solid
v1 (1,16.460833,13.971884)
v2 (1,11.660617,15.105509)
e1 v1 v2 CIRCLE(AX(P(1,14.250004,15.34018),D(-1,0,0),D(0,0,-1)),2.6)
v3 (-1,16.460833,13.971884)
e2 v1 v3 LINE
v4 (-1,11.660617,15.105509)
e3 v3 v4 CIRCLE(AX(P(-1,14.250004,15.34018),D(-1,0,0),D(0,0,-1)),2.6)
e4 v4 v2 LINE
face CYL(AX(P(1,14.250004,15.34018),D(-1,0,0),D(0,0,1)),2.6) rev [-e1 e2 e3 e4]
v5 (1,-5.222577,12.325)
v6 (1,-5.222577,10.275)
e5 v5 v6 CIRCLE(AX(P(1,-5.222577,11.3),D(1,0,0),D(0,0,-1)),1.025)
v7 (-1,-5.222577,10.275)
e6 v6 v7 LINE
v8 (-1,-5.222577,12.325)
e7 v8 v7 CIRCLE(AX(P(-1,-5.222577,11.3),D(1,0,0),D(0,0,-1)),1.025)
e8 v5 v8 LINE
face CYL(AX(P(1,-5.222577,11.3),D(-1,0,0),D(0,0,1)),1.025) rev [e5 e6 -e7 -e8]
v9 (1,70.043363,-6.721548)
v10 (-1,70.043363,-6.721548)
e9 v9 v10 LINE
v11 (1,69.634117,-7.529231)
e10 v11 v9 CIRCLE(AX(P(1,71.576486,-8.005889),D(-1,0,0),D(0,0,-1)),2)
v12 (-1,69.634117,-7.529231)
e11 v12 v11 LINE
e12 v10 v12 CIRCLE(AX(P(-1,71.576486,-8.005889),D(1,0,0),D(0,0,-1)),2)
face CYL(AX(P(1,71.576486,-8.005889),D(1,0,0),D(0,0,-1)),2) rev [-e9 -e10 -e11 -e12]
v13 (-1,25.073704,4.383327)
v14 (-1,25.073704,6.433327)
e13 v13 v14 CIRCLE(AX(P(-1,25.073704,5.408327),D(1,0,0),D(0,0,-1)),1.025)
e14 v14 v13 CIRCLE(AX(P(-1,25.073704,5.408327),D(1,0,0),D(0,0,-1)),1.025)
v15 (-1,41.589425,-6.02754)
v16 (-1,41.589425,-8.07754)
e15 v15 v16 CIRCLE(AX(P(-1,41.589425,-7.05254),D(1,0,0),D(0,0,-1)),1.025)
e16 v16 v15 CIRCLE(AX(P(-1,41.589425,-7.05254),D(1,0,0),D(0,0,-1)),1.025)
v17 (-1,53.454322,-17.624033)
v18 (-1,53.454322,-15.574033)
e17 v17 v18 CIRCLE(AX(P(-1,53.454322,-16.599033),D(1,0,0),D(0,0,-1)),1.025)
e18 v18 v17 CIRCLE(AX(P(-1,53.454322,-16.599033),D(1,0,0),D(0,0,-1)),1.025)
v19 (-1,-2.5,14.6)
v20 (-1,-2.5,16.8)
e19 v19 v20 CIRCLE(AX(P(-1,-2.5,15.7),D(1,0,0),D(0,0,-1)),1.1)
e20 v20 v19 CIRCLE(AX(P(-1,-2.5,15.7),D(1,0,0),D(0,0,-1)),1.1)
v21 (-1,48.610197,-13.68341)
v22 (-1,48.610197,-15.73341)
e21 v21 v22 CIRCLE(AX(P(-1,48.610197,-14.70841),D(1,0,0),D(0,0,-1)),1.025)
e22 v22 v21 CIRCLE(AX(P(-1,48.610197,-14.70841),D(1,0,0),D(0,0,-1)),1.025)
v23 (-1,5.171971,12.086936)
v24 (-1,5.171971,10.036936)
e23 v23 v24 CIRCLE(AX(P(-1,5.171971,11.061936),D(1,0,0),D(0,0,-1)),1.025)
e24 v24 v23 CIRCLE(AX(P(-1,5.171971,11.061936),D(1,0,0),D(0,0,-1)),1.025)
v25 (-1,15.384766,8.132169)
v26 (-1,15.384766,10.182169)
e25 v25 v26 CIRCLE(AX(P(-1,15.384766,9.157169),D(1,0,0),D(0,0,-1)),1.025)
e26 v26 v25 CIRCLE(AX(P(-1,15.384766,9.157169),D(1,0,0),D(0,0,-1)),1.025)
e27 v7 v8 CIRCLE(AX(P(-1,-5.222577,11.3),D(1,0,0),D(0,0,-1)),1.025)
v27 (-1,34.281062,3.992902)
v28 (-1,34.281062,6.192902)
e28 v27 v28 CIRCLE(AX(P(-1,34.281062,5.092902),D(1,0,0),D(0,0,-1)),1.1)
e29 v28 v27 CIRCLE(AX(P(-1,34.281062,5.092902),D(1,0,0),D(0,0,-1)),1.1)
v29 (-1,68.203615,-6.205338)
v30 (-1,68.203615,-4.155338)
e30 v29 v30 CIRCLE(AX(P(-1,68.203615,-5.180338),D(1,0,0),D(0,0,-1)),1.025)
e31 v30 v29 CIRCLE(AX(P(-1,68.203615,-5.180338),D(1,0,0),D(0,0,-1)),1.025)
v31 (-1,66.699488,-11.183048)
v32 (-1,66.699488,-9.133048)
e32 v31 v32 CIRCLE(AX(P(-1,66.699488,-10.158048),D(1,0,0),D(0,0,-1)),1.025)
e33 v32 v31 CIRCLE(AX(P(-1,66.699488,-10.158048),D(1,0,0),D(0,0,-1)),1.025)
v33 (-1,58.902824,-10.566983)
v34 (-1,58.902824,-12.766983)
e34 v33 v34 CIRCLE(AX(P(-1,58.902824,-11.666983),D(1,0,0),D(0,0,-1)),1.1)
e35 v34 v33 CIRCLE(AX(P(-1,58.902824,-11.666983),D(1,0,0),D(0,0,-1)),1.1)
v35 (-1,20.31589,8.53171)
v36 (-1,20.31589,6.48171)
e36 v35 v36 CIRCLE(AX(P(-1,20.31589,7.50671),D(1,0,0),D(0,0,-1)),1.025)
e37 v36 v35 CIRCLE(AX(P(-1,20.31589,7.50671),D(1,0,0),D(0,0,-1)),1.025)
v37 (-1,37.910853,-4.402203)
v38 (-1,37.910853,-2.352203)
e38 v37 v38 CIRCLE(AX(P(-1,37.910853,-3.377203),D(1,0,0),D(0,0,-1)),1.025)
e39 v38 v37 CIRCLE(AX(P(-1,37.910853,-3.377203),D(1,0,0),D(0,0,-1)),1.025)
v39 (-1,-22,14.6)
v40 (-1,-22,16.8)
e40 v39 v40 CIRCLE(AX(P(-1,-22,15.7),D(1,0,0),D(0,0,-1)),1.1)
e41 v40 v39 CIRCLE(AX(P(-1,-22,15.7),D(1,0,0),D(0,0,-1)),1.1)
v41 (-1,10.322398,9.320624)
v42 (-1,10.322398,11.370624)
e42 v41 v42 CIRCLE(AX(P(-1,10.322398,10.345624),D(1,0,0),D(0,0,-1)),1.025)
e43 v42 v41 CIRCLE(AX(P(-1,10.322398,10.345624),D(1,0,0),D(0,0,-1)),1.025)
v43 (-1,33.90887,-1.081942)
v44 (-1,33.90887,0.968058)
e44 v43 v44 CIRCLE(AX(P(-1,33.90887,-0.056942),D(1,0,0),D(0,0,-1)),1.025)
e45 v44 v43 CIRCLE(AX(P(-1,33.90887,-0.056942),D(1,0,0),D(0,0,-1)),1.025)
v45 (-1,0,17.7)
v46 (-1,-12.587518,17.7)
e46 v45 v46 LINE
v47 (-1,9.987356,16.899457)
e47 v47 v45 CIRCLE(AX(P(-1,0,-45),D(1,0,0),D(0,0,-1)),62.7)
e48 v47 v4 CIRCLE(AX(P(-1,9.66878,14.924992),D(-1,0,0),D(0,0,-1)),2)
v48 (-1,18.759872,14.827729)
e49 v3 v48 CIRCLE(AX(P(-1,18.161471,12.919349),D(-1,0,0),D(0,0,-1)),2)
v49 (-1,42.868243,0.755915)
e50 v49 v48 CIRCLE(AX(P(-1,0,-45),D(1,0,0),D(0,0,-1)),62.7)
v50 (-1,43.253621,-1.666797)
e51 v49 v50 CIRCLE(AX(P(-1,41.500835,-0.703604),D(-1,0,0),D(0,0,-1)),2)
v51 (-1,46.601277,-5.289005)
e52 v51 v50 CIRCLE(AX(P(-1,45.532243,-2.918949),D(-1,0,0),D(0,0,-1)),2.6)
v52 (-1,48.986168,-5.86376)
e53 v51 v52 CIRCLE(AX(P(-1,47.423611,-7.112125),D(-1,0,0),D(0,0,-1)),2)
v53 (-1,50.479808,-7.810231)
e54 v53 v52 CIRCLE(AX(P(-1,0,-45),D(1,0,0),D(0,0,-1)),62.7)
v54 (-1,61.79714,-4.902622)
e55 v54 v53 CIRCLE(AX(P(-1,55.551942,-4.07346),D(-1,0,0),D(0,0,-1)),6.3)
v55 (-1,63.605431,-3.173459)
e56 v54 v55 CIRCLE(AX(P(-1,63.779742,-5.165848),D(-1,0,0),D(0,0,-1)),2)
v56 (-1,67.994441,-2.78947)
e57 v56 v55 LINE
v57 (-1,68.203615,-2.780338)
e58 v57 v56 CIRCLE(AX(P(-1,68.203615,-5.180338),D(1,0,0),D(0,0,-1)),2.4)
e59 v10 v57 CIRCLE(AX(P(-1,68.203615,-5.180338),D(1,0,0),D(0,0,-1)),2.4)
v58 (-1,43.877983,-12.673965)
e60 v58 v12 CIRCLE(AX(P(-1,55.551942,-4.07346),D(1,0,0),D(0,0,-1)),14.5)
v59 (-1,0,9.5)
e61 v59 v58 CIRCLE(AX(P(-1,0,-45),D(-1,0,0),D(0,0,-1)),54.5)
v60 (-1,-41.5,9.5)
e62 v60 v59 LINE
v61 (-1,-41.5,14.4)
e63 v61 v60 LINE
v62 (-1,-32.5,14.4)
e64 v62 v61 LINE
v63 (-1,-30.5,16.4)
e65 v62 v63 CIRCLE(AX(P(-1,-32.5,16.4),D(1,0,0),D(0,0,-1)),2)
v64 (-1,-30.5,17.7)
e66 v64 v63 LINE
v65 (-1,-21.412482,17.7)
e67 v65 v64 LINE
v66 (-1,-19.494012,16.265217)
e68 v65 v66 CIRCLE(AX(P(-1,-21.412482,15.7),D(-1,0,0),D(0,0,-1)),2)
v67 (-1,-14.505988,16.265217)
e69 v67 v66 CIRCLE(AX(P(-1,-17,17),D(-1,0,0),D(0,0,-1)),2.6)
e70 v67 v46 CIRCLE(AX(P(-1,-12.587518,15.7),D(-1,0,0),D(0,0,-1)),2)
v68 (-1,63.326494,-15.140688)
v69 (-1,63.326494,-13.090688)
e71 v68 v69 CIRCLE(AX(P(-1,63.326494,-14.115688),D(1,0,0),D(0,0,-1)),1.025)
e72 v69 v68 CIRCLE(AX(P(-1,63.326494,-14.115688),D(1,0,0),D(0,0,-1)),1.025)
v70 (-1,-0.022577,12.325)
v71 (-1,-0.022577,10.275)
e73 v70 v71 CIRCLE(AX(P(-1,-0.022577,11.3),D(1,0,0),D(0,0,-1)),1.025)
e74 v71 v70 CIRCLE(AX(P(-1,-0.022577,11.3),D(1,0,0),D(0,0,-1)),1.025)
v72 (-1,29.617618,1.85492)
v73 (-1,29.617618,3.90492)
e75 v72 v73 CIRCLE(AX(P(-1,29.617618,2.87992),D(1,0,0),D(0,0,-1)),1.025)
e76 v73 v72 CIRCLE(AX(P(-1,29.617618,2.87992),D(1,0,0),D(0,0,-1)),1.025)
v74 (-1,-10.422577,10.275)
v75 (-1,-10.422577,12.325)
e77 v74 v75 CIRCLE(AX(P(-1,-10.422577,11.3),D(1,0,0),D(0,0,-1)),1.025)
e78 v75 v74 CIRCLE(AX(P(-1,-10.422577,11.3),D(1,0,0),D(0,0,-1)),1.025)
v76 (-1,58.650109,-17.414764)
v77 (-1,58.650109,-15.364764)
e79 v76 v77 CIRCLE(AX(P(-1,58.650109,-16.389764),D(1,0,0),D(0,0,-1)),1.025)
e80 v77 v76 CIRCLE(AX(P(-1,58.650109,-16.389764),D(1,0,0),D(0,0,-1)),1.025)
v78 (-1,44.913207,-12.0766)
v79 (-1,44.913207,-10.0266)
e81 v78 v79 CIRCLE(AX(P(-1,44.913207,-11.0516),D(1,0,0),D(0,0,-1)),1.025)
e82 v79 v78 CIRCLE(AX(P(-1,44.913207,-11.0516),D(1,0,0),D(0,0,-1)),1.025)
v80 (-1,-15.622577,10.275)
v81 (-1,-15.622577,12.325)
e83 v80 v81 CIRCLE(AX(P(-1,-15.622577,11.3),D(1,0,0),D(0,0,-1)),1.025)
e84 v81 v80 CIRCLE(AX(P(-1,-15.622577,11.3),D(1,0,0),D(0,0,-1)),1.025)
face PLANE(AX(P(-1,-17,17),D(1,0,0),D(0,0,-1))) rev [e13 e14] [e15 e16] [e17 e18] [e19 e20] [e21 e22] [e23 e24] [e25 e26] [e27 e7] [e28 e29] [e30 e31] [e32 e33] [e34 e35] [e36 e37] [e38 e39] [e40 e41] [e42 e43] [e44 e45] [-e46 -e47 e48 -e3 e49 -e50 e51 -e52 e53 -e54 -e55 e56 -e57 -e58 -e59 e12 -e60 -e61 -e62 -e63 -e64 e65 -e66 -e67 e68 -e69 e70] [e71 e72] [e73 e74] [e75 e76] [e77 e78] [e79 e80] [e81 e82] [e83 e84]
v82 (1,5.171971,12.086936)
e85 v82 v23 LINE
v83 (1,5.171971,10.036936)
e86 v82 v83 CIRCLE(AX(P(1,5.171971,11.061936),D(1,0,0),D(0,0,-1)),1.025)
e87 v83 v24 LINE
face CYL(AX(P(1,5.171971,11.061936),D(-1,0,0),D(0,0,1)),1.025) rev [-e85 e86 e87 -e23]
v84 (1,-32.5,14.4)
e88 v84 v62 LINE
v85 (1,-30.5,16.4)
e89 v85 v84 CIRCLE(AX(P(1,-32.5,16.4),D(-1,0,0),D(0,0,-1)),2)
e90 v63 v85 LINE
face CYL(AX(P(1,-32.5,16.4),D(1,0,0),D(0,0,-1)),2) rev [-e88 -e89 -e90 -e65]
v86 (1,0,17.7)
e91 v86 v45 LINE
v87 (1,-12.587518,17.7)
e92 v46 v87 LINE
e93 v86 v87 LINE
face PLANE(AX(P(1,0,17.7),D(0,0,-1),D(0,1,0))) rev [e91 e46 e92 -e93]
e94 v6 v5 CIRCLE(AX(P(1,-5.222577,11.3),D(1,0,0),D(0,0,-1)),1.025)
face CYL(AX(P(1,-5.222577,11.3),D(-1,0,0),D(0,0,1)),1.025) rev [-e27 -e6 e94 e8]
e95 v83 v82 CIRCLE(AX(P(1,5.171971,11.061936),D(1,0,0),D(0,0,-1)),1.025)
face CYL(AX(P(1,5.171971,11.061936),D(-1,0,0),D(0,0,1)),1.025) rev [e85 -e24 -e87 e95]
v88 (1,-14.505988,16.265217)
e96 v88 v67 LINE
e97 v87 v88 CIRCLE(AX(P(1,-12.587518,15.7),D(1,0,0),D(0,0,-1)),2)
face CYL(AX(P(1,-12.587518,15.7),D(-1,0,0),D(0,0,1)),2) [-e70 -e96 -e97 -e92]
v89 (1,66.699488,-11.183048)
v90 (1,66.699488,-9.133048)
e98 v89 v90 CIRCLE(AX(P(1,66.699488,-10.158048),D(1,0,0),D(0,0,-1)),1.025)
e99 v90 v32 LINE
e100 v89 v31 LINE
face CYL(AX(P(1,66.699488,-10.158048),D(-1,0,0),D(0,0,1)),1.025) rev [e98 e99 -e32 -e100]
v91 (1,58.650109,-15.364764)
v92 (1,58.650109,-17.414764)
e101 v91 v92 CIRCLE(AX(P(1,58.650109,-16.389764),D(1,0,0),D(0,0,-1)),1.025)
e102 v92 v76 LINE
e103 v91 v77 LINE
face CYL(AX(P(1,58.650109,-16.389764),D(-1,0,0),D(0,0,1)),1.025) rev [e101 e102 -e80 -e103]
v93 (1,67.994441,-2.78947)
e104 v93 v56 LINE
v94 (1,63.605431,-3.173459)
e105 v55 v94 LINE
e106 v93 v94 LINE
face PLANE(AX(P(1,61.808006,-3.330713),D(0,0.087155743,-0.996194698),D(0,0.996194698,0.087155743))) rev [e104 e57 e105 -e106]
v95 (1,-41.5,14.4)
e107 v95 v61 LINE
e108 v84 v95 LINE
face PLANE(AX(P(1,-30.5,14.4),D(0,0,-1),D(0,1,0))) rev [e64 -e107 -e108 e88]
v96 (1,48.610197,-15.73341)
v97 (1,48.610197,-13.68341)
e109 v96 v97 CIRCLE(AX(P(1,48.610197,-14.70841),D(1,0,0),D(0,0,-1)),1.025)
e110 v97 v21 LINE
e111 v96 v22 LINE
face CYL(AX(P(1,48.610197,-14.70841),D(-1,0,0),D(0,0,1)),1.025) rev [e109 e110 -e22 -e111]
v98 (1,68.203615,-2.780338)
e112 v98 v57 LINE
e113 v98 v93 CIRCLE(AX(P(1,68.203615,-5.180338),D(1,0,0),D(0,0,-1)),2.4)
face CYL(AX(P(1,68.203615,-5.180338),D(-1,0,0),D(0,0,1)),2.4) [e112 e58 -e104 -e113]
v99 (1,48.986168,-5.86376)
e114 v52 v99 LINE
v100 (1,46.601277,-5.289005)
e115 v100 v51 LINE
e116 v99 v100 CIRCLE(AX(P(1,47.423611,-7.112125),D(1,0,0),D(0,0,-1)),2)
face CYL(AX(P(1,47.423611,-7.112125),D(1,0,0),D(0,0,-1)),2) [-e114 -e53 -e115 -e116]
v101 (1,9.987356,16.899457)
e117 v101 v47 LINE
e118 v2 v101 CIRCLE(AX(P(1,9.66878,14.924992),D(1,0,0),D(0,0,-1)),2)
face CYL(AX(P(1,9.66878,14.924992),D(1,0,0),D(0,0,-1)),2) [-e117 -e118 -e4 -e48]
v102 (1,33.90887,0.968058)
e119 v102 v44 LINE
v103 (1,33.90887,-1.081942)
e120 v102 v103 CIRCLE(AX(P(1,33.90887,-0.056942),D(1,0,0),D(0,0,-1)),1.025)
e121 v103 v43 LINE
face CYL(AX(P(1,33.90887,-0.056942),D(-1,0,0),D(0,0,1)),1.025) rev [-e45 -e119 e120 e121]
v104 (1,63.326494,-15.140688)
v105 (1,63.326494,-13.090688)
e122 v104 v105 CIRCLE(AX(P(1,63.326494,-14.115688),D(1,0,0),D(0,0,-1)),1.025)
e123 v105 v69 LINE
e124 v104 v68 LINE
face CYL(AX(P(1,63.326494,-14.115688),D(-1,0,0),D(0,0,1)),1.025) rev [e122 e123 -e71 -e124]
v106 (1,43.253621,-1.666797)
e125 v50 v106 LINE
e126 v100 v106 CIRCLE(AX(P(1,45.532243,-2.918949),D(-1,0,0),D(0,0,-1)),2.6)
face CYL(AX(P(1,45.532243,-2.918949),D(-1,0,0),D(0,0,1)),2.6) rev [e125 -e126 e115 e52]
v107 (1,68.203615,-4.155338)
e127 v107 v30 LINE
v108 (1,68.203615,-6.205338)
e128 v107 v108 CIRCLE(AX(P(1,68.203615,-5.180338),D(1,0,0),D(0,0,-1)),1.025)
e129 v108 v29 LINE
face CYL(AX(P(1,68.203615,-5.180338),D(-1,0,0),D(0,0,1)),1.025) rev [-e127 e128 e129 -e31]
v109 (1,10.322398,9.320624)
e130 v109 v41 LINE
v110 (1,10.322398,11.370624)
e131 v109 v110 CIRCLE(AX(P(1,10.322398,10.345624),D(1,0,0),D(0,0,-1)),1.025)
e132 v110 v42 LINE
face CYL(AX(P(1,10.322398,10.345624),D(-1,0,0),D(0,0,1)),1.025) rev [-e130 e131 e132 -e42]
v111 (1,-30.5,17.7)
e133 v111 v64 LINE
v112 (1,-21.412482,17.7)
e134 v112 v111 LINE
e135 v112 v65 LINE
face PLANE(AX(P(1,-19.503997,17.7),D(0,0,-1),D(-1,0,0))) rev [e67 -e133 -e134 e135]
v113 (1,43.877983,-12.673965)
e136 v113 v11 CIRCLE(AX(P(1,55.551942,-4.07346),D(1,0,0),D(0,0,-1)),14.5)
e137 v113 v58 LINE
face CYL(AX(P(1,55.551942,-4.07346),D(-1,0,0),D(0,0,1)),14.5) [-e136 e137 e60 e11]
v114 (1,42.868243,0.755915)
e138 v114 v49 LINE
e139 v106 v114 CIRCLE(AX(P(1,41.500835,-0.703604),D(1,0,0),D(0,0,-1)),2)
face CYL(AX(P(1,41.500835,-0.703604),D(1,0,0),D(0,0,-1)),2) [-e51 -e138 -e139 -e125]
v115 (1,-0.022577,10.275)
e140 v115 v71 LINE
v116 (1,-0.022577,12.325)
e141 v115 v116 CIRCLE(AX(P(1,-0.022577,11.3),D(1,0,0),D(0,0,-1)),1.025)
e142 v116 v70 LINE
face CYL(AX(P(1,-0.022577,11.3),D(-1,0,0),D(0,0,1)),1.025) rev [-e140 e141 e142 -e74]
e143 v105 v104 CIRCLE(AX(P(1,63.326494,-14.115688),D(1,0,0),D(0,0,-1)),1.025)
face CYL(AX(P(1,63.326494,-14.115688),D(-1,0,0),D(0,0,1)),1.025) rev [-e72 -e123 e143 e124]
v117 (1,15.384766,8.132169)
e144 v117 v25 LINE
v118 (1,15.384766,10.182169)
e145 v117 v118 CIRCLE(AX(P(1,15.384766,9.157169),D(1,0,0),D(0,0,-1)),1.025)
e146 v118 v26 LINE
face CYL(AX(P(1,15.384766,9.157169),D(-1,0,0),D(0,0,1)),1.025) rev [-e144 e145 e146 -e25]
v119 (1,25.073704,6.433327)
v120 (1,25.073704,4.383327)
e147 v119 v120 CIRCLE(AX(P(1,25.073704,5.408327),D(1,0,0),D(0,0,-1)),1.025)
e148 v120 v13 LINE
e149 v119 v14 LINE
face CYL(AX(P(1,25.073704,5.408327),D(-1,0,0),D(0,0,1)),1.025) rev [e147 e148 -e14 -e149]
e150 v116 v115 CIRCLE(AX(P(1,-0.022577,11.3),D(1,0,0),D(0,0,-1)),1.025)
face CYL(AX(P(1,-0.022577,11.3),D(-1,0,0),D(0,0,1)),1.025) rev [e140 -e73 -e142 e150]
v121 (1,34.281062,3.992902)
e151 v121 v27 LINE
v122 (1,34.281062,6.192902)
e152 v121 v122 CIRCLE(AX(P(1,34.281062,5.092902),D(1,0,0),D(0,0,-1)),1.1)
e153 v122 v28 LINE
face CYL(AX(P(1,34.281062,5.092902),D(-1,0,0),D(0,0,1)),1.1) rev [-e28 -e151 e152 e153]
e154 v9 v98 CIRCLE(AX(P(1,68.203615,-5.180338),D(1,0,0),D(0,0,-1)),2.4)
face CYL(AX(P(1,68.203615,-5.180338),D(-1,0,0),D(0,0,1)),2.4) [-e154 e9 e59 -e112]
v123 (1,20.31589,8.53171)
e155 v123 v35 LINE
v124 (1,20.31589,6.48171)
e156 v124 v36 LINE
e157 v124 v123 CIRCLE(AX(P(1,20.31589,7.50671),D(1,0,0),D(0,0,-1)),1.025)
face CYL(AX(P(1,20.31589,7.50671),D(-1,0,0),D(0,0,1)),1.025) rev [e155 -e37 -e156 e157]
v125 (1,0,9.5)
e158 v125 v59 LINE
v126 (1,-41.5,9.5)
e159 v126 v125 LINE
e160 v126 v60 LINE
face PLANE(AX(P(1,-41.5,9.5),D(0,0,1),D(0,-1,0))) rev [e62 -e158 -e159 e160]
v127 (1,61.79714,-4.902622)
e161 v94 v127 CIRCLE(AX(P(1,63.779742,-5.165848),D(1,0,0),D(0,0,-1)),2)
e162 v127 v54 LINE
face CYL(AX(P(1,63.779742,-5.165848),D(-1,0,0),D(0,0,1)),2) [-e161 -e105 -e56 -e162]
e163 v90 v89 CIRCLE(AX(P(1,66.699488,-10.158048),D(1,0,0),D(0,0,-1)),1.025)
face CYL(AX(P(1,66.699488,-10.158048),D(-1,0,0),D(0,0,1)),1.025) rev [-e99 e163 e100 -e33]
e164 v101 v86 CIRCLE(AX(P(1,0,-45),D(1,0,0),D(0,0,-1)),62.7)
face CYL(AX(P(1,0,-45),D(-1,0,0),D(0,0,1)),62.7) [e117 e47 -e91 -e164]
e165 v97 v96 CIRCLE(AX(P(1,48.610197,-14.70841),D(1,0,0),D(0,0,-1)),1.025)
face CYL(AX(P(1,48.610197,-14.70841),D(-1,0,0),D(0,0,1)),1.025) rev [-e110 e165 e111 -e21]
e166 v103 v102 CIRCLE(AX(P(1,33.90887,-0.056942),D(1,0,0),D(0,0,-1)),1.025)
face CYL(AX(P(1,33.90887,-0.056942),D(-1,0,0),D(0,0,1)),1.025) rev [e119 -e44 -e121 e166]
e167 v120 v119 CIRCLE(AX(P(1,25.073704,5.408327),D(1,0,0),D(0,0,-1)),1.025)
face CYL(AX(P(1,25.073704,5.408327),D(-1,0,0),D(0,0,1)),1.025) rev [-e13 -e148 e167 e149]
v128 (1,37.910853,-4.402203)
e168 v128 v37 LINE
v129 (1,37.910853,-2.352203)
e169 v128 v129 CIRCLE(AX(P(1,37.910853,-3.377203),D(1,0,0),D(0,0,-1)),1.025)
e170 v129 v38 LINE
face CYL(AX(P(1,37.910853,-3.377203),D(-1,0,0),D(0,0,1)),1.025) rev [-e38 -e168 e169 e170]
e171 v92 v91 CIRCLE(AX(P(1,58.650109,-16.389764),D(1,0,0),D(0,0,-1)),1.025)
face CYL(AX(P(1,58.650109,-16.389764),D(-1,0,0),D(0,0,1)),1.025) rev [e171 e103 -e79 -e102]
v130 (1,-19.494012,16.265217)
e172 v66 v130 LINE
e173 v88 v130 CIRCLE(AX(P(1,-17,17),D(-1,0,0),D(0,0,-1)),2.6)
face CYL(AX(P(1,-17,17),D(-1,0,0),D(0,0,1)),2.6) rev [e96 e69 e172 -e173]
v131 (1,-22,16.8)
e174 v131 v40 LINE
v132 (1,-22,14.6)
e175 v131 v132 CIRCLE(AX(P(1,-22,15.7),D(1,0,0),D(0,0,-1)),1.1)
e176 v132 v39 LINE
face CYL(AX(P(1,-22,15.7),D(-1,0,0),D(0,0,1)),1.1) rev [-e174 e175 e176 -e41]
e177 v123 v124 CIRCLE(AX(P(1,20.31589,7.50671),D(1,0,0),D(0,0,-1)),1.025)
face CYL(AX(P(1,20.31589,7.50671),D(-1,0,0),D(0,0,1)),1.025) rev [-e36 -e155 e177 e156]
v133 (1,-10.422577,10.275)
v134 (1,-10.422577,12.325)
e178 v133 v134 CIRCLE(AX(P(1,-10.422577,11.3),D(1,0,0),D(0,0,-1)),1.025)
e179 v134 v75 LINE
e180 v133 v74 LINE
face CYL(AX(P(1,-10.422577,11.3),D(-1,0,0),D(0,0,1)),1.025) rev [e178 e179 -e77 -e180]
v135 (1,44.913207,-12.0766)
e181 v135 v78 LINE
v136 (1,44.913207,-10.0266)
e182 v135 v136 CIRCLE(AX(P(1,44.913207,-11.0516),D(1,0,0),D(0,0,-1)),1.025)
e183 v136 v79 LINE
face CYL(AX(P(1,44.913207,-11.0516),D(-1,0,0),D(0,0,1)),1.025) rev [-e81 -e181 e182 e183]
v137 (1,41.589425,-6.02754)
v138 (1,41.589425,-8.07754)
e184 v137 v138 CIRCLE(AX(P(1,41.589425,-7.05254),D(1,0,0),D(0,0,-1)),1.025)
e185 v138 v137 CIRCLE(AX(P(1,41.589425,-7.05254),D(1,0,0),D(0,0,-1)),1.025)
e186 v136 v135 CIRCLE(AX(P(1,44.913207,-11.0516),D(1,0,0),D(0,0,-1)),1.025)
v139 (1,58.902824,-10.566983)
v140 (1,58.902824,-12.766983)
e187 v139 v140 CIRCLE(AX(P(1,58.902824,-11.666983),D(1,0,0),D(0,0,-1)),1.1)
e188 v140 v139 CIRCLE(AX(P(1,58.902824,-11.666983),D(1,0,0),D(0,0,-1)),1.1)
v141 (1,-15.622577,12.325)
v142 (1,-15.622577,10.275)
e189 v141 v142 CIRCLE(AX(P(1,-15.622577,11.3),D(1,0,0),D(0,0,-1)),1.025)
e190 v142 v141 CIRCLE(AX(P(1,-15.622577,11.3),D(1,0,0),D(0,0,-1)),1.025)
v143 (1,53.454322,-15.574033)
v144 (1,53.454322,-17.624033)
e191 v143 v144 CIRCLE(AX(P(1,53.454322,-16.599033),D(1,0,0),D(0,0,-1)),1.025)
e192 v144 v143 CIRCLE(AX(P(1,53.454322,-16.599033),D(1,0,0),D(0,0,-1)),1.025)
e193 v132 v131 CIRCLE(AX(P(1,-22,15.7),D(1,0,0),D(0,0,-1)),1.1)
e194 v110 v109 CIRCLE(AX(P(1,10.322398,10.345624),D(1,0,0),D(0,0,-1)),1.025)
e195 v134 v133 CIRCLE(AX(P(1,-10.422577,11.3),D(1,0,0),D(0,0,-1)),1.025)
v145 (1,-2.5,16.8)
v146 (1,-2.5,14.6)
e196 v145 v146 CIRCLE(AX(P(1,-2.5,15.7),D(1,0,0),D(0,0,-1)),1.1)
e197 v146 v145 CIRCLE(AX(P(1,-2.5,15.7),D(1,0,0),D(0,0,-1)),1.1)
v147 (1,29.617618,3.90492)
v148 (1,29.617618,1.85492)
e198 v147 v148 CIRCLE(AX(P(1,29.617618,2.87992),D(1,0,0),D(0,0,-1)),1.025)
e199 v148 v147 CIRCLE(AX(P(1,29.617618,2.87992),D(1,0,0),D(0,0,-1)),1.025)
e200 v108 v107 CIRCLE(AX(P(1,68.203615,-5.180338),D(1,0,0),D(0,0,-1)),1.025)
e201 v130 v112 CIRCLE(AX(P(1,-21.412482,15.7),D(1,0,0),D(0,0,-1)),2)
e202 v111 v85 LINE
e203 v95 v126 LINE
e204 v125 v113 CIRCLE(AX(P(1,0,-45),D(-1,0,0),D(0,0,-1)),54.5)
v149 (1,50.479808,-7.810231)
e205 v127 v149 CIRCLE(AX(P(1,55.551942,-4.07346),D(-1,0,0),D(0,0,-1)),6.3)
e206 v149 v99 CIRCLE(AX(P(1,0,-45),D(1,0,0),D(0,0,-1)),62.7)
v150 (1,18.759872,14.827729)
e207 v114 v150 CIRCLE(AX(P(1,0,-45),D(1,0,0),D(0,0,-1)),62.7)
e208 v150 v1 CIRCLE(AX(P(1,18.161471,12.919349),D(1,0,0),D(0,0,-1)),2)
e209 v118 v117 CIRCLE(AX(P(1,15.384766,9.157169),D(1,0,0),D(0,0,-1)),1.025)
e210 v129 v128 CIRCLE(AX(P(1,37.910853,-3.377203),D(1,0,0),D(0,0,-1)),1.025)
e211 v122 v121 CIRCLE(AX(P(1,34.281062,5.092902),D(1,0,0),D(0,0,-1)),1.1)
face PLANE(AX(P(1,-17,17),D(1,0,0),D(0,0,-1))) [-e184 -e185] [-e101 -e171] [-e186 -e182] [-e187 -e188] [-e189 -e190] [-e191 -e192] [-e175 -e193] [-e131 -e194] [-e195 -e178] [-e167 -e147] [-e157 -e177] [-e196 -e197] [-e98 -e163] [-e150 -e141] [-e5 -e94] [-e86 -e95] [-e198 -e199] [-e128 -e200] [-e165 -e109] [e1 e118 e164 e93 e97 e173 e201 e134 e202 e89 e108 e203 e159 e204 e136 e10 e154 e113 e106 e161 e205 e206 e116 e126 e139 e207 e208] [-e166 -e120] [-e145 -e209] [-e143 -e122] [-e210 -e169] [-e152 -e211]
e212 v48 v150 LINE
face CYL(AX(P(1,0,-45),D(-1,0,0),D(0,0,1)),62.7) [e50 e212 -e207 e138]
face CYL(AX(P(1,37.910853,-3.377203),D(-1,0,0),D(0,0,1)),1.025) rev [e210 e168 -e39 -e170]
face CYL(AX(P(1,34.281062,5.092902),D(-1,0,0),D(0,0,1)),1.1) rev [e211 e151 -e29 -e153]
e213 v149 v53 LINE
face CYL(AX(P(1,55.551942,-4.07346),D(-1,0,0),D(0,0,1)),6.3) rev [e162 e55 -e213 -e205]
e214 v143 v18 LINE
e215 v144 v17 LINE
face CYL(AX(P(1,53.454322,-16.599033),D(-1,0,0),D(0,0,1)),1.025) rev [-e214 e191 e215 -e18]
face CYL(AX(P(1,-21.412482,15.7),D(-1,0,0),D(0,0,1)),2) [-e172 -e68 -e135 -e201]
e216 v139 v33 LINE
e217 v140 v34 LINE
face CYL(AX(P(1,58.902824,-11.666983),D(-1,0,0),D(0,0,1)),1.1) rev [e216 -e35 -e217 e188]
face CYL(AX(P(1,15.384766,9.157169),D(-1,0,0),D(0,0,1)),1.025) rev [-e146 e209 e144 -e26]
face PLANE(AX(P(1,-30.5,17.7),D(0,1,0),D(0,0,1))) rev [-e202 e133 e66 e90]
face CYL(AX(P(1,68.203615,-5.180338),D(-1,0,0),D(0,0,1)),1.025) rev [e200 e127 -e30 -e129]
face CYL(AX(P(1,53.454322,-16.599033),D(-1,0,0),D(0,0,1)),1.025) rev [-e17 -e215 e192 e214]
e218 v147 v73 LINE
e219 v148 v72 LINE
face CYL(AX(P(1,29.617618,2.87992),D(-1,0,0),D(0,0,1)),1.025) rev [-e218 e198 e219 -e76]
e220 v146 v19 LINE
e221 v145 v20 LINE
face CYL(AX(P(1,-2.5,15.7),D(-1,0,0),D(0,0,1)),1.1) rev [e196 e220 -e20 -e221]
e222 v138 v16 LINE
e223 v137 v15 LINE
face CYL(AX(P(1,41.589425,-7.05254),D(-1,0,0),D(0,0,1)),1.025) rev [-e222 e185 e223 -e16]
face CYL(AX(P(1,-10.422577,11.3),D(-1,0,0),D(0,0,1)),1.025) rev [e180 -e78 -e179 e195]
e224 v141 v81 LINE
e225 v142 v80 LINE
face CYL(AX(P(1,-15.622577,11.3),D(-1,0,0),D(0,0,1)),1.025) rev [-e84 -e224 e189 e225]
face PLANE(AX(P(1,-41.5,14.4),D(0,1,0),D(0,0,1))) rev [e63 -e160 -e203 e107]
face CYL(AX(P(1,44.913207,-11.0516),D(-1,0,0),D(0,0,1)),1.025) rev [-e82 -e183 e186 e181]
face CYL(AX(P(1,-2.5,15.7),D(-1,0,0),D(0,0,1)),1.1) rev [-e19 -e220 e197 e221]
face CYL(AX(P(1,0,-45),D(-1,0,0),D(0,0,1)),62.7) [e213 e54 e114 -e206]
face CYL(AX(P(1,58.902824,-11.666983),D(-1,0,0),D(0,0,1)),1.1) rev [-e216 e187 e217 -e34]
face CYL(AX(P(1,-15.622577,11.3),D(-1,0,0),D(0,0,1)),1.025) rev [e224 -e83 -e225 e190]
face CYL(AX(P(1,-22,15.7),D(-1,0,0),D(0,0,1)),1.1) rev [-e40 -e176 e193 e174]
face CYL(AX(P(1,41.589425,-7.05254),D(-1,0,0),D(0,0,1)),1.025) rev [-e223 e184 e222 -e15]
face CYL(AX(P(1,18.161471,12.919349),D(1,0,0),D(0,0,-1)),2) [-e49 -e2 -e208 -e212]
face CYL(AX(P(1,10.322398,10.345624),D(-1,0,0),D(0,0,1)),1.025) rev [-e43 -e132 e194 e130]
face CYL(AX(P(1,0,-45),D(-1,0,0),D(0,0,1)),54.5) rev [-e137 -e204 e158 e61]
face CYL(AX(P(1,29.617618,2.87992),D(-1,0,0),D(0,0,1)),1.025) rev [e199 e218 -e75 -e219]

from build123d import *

# Parameters (mm, degrees)
SKETCH_3_R      = 1.025
SKETCH_3_R_2    = 1.1
EXTRUDE_1_DEPTH = 1
FILLET_R2_1_R   = 2


with BuildPart() as part:
    # 草图3 → 凸台-拉伸1 (new, symmetric)
    with BuildSketch(Plane(origin=(0, 0, 0), x_dir=(0, 0, -1), z_dir=(1, 0, 0))):
        with BuildLine():
            Line((-17.7, 0), (-17.7, -14.496003195))
            ThreePointArc((-17.7, -14.496003195), (-14.4, -17), (-17.7, -19.503996805))
            Line((-17.7, -19.503996805), (-17.7, -30.5))
            Line((-17.7, -30.5), (-14.4, -30.5))
            Line((-14.4, -30.5), (-14.4, -41.5))
            Line((-14.4, -41.5), (-9.5, -41.5))
            Line((-9.5, -41.5), (-9.5, 0))
            ThreePointArc((-9.5, 0), (-3.641643332, 24.581304561), (12.673964548, 43.877983453))
            ThreePointArc((12.673964548, 43.877983453), (18.238631052, 58.649993458), (7.015444369, 69.750348117))
            ThreePointArc((7.015444369, 69.750348117), (4.259457791, 70.419913806), (2.78947036, 67.994441237))
            Line((2.78947036, 67.994441237), (3.330713342, 61.80800564))
            ThreePointArc((3.330713342, 61.80800564), (9.932048157, 57.868608346), (7.810230773, 50.479808487))
            ThreePointArc((7.810230773, 50.479808487), (6.044157033, 49.12974963), (4.327051221, 47.71793413))
            ThreePointArc((4.327051221, 47.71793413), (4.683637937, 43.62282602), (0.629267836, 44.300430327))
            ThreePointArc((0.629267836, 44.300430327), (-9.150529626, 31.607121685), (-15.393591082, 16.849455665))
            ThreePointArc((-15.393591082, 16.849455665), (-12.809785788, 13.652423491), (-16.550868347, 11.949083889))
            ThreePointArc((-16.550868347, 11.949083889), (-17.412055908, 6.002106075), (-17.7, 0))
        make_face()
        with Locations((5.180337635, 68.203615019)):
            Circle(SKETCH_3_R, mode=Mode.SUBTRACT)
        with Locations((-15.7, -22)):
            Circle(SKETCH_3_R_2, mode=Mode.SUBTRACT)
        with Locations((-15.7, -2.5)):
            Circle(SKETCH_3_R_2, mode=Mode.SUBTRACT)
        with Locations((-5.092901527, 34.281062069)):
            Circle(SKETCH_3_R_2, mode=Mode.SUBTRACT)
        with Locations((11.666982528, 58.902824492)):
            Circle(SKETCH_3_R_2, mode=Mode.SUBTRACT)
        with Locations((10.158048255, 66.699488368)):
            Circle(SKETCH_3_R, mode=Mode.SUBTRACT)
        with Locations((14.115687733, 63.326494185)):
            Circle(SKETCH_3_R, mode=Mode.SUBTRACT)
        with Locations((16.389764399, 58.650109329)):
            Circle(SKETCH_3_R, mode=Mode.SUBTRACT)
        with Locations((16.599033086, 53.454321938)):
            Circle(SKETCH_3_R, mode=Mode.SUBTRACT)
        with Locations((14.708410246, 48.610197117)):
            Circle(SKETCH_3_R, mode=Mode.SUBTRACT)
        with Locations((11.051599939, 44.913206669)):
            Circle(SKETCH_3_R, mode=Mode.SUBTRACT)
        with Locations((7.05254031, 41.589425376)):
            Circle(SKETCH_3_R, mode=Mode.SUBTRACT)
        with Locations((3.377202973, 37.9108529)):
            Circle(SKETCH_3_R, mode=Mode.SUBTRACT)
        with Locations((0.056941504, 33.908870419)):
            Circle(SKETCH_3_R, mode=Mode.SUBTRACT)
        with Locations((-2.879919599, 29.617618054)):
            Circle(SKETCH_3_R, mode=Mode.SUBTRACT)
        with Locations((-5.408326555, 25.073703633)):
            Circle(SKETCH_3_R, mode=Mode.SUBTRACT)
        with Locations((-7.506710024, 20.315890394)):
            Circle(SKETCH_3_R, mode=Mode.SUBTRACT)
        with Locations((-9.157169108, 15.384766302)):
            Circle(SKETCH_3_R, mode=Mode.SUBTRACT)
        with Locations((-10.345624069, 10.322397804)):
            Circle(SKETCH_3_R, mode=Mode.SUBTRACT)
        with Locations((-11.06193643, 5.171970967)):
            Circle(SKETCH_3_R, mode=Mode.SUBTRACT)
        with Locations((-11.3, -0.022576726)):
            Circle(SKETCH_3_R, mode=Mode.SUBTRACT)
        with Locations((-11.3, -5.222576726)):
            Circle(SKETCH_3_R, mode=Mode.SUBTRACT)
        with Locations((-11.3, -10.422576726)):
            Circle(SKETCH_3_R, mode=Mode.SUBTRACT)
        with Locations((-11.3, -15.622576726)):
            Circle(SKETCH_3_R, mode=Mode.SUBTRACT)
    extrude(amount=EXTRUDE_1_DEPTH, both=True)

    # R2 圆角1
    fillet_r2_1_edges = [part.edges().sort_by_distance(p)[0] for p in [
        (0, -14.496003195, 17.7),
        (0, 11.949083889, 16.550868347),
        (0, 16.849455665, 15.393591082),
        (0, 44.300430327, -0.629267836),
        (0, 47.71793413, -4.327051221),
        (0, 61.80800564, -3.330713342),
        (0, 69.750348117, -7.015444369),
        (0, -30.5, 14.4),
        (0, -19.503996805, 17.7),
    ]]
    fillet(fillet_r2_1_edges, radius=FILLET_R2_1_R)


solid = part.part
